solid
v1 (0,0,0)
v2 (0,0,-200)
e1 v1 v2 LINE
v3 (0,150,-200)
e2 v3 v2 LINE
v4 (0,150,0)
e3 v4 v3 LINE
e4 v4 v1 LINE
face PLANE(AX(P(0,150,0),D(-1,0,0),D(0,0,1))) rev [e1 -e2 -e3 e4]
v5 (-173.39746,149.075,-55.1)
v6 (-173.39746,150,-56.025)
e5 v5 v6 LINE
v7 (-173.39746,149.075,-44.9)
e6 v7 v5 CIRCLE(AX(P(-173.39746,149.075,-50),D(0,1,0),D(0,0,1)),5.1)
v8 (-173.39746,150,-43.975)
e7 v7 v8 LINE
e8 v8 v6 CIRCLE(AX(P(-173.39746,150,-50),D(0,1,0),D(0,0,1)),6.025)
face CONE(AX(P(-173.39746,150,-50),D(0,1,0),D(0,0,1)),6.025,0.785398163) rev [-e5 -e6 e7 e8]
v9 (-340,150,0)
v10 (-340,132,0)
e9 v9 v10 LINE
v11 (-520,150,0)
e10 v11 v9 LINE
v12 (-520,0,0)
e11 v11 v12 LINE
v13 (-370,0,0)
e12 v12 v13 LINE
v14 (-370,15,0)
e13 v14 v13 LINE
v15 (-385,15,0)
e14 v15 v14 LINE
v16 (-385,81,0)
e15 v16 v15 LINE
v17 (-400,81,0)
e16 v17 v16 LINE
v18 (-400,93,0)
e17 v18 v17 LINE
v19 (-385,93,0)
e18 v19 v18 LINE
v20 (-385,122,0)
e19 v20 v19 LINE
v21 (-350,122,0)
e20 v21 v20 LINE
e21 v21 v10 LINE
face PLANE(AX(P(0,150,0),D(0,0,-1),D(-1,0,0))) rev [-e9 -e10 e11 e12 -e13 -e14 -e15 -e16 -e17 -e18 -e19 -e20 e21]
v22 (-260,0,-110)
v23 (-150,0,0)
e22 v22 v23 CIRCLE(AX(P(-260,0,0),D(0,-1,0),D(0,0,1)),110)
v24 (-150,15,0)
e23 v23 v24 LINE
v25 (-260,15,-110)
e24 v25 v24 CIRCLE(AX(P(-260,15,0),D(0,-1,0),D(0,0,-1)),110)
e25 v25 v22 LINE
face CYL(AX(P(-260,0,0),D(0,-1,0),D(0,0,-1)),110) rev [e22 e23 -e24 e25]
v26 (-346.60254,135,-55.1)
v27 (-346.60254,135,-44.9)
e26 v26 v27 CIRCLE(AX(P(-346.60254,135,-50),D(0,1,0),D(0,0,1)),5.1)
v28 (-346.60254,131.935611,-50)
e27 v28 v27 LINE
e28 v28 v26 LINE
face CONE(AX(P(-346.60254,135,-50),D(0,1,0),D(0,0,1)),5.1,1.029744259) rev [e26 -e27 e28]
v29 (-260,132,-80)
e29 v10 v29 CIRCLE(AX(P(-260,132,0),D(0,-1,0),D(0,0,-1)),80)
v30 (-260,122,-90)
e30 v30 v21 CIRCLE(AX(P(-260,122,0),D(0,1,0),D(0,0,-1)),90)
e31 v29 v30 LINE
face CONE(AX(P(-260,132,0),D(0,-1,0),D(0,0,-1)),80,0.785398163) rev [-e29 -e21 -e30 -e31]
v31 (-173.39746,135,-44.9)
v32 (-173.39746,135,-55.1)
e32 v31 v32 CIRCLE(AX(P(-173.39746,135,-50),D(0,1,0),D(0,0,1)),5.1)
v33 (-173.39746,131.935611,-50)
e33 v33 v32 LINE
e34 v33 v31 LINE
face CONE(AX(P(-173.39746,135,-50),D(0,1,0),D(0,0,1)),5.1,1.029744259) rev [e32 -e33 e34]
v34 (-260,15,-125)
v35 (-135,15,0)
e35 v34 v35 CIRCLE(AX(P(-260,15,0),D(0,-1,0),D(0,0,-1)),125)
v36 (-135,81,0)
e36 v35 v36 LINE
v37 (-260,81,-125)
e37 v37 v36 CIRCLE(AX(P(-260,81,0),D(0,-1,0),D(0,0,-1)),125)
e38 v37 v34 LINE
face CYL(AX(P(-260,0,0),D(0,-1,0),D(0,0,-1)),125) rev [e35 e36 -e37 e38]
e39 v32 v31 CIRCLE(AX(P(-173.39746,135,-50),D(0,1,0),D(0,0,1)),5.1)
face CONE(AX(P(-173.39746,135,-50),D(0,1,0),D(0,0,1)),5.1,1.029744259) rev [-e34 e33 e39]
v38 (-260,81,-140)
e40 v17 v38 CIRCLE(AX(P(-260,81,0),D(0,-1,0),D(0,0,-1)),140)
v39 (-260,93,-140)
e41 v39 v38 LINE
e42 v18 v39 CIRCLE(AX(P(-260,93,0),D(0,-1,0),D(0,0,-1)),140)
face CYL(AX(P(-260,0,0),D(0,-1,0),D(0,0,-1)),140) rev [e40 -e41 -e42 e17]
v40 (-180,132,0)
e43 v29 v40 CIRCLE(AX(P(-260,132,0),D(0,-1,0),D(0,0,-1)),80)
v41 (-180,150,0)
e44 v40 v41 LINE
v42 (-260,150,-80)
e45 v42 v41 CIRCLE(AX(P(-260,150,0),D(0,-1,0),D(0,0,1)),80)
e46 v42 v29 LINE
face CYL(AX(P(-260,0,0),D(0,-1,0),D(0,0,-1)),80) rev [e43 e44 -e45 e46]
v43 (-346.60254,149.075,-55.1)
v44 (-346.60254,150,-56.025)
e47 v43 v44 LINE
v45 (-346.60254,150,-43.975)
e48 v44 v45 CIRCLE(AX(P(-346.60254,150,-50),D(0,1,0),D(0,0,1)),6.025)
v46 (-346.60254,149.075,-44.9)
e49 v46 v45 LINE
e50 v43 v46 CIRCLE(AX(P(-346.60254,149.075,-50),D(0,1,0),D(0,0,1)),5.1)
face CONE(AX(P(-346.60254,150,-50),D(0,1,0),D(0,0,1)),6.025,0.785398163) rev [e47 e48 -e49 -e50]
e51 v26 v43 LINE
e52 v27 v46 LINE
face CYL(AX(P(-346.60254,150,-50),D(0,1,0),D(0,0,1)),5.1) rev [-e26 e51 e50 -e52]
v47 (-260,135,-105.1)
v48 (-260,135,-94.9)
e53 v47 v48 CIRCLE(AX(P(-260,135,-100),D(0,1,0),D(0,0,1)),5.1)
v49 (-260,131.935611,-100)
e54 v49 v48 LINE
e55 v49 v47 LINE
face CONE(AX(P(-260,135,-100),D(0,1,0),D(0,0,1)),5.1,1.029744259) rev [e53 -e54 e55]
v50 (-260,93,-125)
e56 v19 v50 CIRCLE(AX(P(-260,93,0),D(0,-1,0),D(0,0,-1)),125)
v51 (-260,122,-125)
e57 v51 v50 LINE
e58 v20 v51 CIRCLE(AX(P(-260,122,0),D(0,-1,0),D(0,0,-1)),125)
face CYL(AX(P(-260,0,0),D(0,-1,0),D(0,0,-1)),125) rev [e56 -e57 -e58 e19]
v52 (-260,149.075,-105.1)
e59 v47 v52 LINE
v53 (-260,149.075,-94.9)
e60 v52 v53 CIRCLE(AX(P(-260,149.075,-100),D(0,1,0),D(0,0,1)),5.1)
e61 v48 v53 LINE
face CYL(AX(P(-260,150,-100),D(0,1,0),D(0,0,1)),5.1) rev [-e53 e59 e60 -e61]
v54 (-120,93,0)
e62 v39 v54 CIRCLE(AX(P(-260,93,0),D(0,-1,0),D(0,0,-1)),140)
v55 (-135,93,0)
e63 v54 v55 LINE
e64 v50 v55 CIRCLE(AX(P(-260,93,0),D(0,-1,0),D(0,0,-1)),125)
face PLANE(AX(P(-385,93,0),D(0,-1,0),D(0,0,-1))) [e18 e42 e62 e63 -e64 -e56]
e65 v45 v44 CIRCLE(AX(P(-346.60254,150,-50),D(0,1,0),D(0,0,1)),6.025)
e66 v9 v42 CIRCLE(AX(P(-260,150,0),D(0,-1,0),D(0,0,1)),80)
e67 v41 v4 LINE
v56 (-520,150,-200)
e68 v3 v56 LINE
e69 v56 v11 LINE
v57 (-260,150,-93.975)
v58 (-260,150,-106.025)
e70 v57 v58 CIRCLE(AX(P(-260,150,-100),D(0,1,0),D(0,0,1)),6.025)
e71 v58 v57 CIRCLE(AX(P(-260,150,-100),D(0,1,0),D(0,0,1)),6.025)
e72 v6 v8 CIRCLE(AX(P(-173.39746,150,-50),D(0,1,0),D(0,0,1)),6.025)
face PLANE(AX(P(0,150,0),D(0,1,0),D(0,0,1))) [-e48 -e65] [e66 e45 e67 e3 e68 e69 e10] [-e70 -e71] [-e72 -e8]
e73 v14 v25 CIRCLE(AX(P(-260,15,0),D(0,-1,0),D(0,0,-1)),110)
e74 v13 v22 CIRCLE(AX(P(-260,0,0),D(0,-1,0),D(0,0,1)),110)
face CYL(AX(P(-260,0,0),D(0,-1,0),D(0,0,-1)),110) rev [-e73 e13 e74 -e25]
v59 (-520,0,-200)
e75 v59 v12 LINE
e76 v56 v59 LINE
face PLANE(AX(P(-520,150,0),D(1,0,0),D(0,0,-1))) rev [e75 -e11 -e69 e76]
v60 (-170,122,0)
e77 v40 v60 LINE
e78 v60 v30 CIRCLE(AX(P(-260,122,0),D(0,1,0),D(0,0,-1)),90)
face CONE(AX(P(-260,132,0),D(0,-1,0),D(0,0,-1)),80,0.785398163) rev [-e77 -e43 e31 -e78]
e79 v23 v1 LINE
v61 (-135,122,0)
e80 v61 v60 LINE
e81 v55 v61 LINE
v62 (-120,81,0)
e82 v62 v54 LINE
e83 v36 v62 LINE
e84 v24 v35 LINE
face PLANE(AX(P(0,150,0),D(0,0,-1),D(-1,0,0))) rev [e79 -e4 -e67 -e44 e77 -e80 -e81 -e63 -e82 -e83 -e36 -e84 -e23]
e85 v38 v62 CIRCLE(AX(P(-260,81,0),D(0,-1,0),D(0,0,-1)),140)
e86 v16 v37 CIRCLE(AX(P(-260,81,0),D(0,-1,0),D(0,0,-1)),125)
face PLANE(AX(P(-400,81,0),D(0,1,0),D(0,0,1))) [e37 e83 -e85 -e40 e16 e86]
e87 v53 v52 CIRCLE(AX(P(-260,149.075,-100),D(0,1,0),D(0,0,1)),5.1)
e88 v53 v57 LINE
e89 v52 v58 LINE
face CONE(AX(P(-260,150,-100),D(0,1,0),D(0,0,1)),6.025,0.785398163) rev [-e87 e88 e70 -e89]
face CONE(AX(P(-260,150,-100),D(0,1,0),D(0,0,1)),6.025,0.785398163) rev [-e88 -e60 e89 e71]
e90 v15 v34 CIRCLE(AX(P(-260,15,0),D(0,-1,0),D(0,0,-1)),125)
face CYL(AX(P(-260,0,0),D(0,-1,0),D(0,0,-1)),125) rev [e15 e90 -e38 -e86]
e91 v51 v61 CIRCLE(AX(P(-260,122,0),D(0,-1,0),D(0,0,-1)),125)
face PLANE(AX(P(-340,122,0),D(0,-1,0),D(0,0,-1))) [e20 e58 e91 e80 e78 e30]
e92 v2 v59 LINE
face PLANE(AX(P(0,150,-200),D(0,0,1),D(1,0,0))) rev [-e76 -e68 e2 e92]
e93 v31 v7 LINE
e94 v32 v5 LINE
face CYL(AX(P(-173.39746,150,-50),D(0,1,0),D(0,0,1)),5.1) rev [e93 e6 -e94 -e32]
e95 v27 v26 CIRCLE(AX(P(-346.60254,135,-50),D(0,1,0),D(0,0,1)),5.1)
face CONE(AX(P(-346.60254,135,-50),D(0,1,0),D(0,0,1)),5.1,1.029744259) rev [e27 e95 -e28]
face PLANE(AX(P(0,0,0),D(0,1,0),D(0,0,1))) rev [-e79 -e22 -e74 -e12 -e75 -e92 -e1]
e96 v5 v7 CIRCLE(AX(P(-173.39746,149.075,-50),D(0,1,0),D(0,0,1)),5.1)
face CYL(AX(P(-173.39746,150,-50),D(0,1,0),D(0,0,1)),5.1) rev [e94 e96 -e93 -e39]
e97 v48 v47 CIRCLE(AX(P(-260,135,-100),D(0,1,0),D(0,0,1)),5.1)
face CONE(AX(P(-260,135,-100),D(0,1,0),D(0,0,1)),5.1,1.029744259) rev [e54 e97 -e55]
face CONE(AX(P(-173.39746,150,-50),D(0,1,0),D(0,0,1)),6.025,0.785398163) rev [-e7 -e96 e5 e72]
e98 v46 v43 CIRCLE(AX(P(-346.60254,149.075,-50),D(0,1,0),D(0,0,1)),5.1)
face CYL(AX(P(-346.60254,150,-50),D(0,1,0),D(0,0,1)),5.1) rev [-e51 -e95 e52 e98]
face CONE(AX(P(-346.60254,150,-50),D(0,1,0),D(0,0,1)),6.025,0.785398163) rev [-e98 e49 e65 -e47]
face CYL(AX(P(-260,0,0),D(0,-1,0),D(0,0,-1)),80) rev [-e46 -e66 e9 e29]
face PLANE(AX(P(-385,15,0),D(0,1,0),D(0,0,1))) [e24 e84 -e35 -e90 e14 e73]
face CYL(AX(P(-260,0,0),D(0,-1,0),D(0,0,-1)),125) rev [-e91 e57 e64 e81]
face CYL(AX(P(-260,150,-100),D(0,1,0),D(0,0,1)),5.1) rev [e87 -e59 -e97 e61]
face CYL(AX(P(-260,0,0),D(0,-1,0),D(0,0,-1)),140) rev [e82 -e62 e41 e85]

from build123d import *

# Parameters (mm, degrees)
SKETCH_1_W                    = 520
SKETCH_1_H                    = 200
EXTRUDE_1_DEPTH               = 150
HOLE_WIZARD_M12_1_D           = 10.2
HOLE_WIZARD_M12_1_DEPTH       = 15
HOLE_WIZARD_M12_1_CSINK_D     = 12.05
HOLE_WIZARD_M12_1_CSINK_ANGLE = 90
HOLE_WIZARD_M12_1_TIP         = 3.064389157
CHAMFER_1_SIZE                = 10


with BuildPart() as part:
    # 草图1 → 凸台-拉伸1 (new body)
    with BuildSketch(Plane(origin=(0, 0, 0), x_dir=(1, 0, 0), z_dir=(0, 1, 0))):
        with Locations((-260, 100)):
            Rectangle(SKETCH_1_W, SKETCH_1_H)
    extrude(amount=EXTRUDE_1_DEPTH)

    # M12 螺纹孔1
    with Locations(Plane(origin=(0, 150, 0), x_dir=(1, 0, 0), z_dir=(0, 1, 0))):
        with Locations((-260, 100), (-173.397459622, 50), (-346.602540378, 50)):
            CounterSinkHole(HOLE_WIZARD_M12_1_D / 2, HOLE_WIZARD_M12_1_CSINK_D / 2, depth=HOLE_WIZARD_M12_1_DEPTH, counter_sink_angle=HOLE_WIZARD_M12_1_CSINK_ANGLE)
            with Locations((0, 0, -(HOLE_WIZARD_M12_1_DEPTH + HOLE_WIZARD_M12_1_TIP / 2))):  # 118° drill point
                Cone(0, HOLE_WIZARD_M12_1_D / 2, HOLE_WIZARD_M12_1_TIP, mode=Mode.SUBTRACT)

    # 草图6 → 切除-旋转1 (revolve, cut)
    with BuildSketch(Plane.XY):
        Polygon((-260, 150), (-340, 150), (-340, 122), (-385, 122), (-385, 93), (-400, 93), (-400, 81), (-385, 81), (-385, 15), (-370, 15), (-370, 0), (-260, 0), align=None)
    revolve(axis=Axis((-260, 0, 0), (0, 1, 0)), mode=Mode.SUBTRACT)

    # 倒角1
    chamfer_1_edges = [part.edges().sort_by_distance(p)[0] for p in [
        (-260, 122, -80),
    ]]
    chamfer(chamfer_1_edges, length=CHAMFER_1_SIZE)


solid = part.part
